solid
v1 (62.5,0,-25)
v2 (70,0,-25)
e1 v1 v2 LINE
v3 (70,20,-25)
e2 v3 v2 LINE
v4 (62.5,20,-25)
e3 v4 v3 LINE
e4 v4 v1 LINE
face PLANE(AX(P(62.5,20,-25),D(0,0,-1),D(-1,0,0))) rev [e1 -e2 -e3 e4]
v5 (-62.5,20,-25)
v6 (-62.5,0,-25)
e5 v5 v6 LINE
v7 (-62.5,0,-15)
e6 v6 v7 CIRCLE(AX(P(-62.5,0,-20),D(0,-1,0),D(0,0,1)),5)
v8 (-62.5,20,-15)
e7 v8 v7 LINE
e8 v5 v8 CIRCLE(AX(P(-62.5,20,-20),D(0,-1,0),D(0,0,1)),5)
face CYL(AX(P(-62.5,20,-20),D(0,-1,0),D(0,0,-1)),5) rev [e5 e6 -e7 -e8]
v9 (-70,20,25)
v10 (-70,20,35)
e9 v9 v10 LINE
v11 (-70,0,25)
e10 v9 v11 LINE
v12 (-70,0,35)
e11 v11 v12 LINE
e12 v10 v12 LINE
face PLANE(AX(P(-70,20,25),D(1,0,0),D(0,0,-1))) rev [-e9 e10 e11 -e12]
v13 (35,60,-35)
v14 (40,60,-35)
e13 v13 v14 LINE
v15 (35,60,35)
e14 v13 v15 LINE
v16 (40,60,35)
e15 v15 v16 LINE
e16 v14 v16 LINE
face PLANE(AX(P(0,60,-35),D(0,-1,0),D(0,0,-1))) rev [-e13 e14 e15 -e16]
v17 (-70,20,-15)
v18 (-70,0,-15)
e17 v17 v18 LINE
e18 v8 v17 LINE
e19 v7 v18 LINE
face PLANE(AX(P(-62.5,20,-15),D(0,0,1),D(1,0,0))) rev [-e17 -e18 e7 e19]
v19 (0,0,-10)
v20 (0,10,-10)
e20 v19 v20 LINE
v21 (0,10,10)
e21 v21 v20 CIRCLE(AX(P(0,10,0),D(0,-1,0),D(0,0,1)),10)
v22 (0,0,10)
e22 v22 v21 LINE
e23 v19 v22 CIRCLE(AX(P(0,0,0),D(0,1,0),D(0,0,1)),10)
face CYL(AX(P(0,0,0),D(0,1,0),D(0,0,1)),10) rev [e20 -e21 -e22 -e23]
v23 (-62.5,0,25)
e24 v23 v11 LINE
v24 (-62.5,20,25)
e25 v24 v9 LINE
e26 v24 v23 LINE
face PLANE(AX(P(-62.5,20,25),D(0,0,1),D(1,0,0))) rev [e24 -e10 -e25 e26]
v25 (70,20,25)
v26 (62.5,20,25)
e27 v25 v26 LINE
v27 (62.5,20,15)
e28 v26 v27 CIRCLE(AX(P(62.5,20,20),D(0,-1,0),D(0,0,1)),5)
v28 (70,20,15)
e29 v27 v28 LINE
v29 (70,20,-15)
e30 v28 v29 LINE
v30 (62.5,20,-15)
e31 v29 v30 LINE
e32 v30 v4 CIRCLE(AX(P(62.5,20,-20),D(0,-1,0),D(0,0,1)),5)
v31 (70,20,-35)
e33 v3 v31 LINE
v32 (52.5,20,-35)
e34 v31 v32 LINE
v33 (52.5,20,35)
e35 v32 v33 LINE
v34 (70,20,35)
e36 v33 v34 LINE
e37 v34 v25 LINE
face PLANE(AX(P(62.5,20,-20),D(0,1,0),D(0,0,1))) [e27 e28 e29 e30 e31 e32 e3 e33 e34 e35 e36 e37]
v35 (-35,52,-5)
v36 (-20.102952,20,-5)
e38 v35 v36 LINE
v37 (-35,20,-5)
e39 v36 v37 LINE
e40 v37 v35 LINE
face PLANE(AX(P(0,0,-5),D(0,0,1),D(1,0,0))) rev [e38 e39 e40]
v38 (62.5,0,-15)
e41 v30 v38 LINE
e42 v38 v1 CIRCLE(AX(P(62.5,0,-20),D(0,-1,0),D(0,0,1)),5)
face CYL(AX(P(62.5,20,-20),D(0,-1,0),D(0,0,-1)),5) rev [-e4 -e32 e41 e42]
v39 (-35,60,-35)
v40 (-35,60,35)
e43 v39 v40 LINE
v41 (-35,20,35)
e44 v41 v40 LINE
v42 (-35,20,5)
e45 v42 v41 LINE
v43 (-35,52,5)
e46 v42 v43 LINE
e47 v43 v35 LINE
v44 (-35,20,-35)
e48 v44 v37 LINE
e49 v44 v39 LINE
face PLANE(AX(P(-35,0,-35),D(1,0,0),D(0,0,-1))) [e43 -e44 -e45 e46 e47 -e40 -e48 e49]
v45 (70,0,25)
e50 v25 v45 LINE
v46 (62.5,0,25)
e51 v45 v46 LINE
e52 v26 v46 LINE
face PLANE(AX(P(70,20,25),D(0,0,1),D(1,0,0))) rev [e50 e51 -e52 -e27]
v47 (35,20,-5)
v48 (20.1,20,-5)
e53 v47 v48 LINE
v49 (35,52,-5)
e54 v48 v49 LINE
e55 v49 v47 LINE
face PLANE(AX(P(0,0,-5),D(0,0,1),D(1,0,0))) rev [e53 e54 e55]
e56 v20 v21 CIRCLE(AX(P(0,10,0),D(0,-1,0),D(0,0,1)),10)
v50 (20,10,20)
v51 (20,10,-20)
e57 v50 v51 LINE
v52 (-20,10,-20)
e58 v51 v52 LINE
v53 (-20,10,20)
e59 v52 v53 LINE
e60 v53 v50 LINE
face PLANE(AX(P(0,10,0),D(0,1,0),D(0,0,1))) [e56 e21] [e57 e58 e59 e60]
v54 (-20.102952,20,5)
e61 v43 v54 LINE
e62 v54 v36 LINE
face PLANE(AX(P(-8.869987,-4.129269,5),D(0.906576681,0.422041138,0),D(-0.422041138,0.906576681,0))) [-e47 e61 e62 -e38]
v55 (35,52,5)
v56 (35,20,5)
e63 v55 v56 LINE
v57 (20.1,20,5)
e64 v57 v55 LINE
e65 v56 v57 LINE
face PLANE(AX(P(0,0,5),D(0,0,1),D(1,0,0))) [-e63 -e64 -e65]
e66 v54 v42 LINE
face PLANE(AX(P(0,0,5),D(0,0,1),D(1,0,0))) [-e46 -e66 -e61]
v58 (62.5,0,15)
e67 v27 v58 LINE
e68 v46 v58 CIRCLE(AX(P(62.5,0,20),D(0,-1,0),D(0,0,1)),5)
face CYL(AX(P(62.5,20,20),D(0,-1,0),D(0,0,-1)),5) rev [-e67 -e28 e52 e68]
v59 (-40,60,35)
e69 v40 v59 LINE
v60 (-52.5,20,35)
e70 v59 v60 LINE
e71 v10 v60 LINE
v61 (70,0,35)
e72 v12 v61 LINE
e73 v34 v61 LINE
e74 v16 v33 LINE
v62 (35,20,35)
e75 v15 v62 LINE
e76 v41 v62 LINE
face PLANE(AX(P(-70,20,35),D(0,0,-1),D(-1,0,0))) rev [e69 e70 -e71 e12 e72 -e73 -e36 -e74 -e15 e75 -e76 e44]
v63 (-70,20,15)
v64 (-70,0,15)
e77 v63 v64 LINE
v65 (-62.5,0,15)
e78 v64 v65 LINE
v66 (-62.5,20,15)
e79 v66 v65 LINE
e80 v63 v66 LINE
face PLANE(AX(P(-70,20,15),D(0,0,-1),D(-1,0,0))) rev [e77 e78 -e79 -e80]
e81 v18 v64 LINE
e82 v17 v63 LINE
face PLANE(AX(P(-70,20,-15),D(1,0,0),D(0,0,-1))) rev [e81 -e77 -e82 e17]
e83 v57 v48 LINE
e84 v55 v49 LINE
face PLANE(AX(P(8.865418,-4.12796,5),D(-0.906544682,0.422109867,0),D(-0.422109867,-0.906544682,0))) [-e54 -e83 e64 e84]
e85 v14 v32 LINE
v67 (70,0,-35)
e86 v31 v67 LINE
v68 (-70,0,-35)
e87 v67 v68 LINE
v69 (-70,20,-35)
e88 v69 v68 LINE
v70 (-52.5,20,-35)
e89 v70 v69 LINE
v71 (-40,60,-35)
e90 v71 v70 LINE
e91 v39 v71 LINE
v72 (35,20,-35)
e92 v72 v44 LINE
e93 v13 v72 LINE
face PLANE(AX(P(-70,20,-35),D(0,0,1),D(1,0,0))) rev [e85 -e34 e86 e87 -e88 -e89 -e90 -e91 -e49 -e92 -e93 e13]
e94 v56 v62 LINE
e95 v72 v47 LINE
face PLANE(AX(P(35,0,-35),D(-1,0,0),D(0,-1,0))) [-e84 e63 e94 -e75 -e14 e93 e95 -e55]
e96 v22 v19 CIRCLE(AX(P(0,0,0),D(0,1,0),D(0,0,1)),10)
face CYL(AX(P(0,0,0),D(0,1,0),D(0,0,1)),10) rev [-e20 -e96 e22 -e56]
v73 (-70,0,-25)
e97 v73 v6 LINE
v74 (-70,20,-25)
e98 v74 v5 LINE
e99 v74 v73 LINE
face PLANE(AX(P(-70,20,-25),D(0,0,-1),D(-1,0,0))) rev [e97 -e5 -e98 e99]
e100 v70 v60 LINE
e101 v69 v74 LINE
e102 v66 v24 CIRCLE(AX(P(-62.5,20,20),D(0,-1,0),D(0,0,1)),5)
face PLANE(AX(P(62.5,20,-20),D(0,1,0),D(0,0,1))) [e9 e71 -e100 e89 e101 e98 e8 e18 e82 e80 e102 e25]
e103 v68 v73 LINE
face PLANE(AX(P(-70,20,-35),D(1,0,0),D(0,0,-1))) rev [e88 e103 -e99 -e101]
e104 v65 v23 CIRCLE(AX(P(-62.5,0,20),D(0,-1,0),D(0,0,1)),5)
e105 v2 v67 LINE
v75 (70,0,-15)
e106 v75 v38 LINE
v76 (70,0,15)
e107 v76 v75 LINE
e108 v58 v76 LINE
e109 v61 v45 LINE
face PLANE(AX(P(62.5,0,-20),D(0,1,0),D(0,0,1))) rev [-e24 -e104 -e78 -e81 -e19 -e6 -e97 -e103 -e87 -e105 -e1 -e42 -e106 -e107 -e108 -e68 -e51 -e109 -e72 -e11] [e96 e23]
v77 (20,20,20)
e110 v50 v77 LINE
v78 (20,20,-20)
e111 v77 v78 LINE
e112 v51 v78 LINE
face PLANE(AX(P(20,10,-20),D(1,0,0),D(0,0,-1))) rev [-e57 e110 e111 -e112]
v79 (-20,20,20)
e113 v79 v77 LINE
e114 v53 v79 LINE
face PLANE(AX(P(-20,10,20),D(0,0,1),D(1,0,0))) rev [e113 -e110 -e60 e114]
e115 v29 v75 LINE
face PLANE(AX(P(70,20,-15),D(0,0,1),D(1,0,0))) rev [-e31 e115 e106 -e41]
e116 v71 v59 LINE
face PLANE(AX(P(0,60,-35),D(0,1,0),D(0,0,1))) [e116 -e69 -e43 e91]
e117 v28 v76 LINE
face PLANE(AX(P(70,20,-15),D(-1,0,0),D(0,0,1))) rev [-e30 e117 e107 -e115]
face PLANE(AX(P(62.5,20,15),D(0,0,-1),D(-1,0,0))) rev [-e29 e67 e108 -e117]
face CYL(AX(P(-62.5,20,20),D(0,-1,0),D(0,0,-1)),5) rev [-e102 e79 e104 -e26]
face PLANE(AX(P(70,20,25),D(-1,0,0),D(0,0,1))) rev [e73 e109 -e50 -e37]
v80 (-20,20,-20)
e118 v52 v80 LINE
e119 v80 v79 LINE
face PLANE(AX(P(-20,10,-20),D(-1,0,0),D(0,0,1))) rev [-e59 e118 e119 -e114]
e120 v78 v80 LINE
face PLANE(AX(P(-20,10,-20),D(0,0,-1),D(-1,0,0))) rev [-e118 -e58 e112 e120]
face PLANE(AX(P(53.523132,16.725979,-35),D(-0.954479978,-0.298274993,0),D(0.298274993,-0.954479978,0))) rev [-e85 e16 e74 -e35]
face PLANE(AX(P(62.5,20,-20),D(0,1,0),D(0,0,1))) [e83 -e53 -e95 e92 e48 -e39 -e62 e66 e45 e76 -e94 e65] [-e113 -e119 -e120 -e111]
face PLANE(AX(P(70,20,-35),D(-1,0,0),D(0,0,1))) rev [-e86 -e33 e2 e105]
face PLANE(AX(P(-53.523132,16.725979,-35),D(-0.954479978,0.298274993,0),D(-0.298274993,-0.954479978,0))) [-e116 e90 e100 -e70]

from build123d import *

# Parameters (mm, degrees)
BASE_PLATE_140X70X20_DEPTH   = 20
CENTRE_HOLE_SKETCH_R         = 10
CENTRE_HOLE_20_DEPTH         = 20
CENTRE_POCKET_SKETCH_W       = 40
CENTRE_POCKET_SKETCH_H       = 40
CENTRE_POCKET_40X40X10_DEPTH = 10
V_BLOCK_UPRIGHTS_DEPTH       = 70
GUSSET_RIB_DEPTH             = 5


with BuildPart() as part:
    # Base Plate Sketch → Base Plate 140x70x20 (new body)
    with BuildSketch(Plane(origin=(0, 0, 0), x_dir=(1, 0, 0), z_dir=(0, 1, 0))):
        with BuildLine():
            Line((-70, 25), (-62.5, 25))
            ThreePointArc((-62.5, 25), (-57.5, 20), (-62.5, 15))
            Line((-62.5, 15), (-70, 15))
            Line((-70, 15), (-70, -15))
            Line((-70, -15), (-62.5, -15))
            ThreePointArc((-62.5, -15), (-57.5, -20), (-62.5, -25))
            Line((-62.5, -25), (-70, -25))
            Line((-70, -25), (-70, -35))
            Line((-70, -35), (70, -35))
            Line((70, -35), (70, -25))
            Line((70, -25), (62.5, -25))
            ThreePointArc((62.5, -25), (57.5, -20), (62.5, -15))
            Line((62.5, -15), (70, -15))
            Line((70, -15), (70, 15))
            Line((70, 15), (62.5, 15))
            ThreePointArc((62.5, 15), (57.5, 20), (62.5, 25))
            Line((62.5, 25), (70, 25))
            Line((70, 25), (70, 35))
            Line((70, 35), (-70, 35))
            Line((-70, 35), (-70, 25))
        make_face()
    extrude(amount=BASE_PLATE_140X70X20_DEPTH)

    # Centre Hole Sketch → Centre Hole Ø20 (cut)
    with BuildSketch(Plane(origin=(0, 20, 0), x_dir=(1, 0, 0), z_dir=(0, 1, 0))):
        with Locations(Location((0, 0, 0), (0, 0, 270))):
            Circle(CENTRE_HOLE_SKETCH_R)
    extrude(amount=-CENTRE_HOLE_20_DEPTH, mode=Mode.SUBTRACT)

    # Centre Pocket Sketch → Centre Pocket 40x40x10 (cut)
    with BuildSketch(Plane(origin=(0, 20, 0), x_dir=(1, 0, 0), z_dir=(0, 1, 0))):
        Rectangle(CENTRE_POCKET_SKETCH_W, CENTRE_POCKET_SKETCH_H)
    extrude(amount=-CENTRE_POCKET_40X40X10_DEPTH, mode=Mode.SUBTRACT)

    # V-Block Uprights Sketch → V-Block Uprights (add)
    with BuildSketch(Plane.XY.offset(35)):
        Polygon((-40, 60), (-52.5, 20), (-35, 20), (-35, 60), align=None)
        Polygon((35, 60), (35, 20), (52.5, 20), (40, 60), align=None)
    extrude(amount=-V_BLOCK_UPRIGHTS_DEPTH)

    # Gusset Rib Sketch → Gusset Rib (add, symmetric)
    with BuildSketch(Plane.XY):
        Polygon((-20.102951906, 20), (-35, 20), (-35, 52), align=None)
        Polygon((20.1, 20), (35, 52), (35, 20), align=None)
    extrude(amount=GUSSET_RIB_DEPTH, both=True)


solid = part.part
